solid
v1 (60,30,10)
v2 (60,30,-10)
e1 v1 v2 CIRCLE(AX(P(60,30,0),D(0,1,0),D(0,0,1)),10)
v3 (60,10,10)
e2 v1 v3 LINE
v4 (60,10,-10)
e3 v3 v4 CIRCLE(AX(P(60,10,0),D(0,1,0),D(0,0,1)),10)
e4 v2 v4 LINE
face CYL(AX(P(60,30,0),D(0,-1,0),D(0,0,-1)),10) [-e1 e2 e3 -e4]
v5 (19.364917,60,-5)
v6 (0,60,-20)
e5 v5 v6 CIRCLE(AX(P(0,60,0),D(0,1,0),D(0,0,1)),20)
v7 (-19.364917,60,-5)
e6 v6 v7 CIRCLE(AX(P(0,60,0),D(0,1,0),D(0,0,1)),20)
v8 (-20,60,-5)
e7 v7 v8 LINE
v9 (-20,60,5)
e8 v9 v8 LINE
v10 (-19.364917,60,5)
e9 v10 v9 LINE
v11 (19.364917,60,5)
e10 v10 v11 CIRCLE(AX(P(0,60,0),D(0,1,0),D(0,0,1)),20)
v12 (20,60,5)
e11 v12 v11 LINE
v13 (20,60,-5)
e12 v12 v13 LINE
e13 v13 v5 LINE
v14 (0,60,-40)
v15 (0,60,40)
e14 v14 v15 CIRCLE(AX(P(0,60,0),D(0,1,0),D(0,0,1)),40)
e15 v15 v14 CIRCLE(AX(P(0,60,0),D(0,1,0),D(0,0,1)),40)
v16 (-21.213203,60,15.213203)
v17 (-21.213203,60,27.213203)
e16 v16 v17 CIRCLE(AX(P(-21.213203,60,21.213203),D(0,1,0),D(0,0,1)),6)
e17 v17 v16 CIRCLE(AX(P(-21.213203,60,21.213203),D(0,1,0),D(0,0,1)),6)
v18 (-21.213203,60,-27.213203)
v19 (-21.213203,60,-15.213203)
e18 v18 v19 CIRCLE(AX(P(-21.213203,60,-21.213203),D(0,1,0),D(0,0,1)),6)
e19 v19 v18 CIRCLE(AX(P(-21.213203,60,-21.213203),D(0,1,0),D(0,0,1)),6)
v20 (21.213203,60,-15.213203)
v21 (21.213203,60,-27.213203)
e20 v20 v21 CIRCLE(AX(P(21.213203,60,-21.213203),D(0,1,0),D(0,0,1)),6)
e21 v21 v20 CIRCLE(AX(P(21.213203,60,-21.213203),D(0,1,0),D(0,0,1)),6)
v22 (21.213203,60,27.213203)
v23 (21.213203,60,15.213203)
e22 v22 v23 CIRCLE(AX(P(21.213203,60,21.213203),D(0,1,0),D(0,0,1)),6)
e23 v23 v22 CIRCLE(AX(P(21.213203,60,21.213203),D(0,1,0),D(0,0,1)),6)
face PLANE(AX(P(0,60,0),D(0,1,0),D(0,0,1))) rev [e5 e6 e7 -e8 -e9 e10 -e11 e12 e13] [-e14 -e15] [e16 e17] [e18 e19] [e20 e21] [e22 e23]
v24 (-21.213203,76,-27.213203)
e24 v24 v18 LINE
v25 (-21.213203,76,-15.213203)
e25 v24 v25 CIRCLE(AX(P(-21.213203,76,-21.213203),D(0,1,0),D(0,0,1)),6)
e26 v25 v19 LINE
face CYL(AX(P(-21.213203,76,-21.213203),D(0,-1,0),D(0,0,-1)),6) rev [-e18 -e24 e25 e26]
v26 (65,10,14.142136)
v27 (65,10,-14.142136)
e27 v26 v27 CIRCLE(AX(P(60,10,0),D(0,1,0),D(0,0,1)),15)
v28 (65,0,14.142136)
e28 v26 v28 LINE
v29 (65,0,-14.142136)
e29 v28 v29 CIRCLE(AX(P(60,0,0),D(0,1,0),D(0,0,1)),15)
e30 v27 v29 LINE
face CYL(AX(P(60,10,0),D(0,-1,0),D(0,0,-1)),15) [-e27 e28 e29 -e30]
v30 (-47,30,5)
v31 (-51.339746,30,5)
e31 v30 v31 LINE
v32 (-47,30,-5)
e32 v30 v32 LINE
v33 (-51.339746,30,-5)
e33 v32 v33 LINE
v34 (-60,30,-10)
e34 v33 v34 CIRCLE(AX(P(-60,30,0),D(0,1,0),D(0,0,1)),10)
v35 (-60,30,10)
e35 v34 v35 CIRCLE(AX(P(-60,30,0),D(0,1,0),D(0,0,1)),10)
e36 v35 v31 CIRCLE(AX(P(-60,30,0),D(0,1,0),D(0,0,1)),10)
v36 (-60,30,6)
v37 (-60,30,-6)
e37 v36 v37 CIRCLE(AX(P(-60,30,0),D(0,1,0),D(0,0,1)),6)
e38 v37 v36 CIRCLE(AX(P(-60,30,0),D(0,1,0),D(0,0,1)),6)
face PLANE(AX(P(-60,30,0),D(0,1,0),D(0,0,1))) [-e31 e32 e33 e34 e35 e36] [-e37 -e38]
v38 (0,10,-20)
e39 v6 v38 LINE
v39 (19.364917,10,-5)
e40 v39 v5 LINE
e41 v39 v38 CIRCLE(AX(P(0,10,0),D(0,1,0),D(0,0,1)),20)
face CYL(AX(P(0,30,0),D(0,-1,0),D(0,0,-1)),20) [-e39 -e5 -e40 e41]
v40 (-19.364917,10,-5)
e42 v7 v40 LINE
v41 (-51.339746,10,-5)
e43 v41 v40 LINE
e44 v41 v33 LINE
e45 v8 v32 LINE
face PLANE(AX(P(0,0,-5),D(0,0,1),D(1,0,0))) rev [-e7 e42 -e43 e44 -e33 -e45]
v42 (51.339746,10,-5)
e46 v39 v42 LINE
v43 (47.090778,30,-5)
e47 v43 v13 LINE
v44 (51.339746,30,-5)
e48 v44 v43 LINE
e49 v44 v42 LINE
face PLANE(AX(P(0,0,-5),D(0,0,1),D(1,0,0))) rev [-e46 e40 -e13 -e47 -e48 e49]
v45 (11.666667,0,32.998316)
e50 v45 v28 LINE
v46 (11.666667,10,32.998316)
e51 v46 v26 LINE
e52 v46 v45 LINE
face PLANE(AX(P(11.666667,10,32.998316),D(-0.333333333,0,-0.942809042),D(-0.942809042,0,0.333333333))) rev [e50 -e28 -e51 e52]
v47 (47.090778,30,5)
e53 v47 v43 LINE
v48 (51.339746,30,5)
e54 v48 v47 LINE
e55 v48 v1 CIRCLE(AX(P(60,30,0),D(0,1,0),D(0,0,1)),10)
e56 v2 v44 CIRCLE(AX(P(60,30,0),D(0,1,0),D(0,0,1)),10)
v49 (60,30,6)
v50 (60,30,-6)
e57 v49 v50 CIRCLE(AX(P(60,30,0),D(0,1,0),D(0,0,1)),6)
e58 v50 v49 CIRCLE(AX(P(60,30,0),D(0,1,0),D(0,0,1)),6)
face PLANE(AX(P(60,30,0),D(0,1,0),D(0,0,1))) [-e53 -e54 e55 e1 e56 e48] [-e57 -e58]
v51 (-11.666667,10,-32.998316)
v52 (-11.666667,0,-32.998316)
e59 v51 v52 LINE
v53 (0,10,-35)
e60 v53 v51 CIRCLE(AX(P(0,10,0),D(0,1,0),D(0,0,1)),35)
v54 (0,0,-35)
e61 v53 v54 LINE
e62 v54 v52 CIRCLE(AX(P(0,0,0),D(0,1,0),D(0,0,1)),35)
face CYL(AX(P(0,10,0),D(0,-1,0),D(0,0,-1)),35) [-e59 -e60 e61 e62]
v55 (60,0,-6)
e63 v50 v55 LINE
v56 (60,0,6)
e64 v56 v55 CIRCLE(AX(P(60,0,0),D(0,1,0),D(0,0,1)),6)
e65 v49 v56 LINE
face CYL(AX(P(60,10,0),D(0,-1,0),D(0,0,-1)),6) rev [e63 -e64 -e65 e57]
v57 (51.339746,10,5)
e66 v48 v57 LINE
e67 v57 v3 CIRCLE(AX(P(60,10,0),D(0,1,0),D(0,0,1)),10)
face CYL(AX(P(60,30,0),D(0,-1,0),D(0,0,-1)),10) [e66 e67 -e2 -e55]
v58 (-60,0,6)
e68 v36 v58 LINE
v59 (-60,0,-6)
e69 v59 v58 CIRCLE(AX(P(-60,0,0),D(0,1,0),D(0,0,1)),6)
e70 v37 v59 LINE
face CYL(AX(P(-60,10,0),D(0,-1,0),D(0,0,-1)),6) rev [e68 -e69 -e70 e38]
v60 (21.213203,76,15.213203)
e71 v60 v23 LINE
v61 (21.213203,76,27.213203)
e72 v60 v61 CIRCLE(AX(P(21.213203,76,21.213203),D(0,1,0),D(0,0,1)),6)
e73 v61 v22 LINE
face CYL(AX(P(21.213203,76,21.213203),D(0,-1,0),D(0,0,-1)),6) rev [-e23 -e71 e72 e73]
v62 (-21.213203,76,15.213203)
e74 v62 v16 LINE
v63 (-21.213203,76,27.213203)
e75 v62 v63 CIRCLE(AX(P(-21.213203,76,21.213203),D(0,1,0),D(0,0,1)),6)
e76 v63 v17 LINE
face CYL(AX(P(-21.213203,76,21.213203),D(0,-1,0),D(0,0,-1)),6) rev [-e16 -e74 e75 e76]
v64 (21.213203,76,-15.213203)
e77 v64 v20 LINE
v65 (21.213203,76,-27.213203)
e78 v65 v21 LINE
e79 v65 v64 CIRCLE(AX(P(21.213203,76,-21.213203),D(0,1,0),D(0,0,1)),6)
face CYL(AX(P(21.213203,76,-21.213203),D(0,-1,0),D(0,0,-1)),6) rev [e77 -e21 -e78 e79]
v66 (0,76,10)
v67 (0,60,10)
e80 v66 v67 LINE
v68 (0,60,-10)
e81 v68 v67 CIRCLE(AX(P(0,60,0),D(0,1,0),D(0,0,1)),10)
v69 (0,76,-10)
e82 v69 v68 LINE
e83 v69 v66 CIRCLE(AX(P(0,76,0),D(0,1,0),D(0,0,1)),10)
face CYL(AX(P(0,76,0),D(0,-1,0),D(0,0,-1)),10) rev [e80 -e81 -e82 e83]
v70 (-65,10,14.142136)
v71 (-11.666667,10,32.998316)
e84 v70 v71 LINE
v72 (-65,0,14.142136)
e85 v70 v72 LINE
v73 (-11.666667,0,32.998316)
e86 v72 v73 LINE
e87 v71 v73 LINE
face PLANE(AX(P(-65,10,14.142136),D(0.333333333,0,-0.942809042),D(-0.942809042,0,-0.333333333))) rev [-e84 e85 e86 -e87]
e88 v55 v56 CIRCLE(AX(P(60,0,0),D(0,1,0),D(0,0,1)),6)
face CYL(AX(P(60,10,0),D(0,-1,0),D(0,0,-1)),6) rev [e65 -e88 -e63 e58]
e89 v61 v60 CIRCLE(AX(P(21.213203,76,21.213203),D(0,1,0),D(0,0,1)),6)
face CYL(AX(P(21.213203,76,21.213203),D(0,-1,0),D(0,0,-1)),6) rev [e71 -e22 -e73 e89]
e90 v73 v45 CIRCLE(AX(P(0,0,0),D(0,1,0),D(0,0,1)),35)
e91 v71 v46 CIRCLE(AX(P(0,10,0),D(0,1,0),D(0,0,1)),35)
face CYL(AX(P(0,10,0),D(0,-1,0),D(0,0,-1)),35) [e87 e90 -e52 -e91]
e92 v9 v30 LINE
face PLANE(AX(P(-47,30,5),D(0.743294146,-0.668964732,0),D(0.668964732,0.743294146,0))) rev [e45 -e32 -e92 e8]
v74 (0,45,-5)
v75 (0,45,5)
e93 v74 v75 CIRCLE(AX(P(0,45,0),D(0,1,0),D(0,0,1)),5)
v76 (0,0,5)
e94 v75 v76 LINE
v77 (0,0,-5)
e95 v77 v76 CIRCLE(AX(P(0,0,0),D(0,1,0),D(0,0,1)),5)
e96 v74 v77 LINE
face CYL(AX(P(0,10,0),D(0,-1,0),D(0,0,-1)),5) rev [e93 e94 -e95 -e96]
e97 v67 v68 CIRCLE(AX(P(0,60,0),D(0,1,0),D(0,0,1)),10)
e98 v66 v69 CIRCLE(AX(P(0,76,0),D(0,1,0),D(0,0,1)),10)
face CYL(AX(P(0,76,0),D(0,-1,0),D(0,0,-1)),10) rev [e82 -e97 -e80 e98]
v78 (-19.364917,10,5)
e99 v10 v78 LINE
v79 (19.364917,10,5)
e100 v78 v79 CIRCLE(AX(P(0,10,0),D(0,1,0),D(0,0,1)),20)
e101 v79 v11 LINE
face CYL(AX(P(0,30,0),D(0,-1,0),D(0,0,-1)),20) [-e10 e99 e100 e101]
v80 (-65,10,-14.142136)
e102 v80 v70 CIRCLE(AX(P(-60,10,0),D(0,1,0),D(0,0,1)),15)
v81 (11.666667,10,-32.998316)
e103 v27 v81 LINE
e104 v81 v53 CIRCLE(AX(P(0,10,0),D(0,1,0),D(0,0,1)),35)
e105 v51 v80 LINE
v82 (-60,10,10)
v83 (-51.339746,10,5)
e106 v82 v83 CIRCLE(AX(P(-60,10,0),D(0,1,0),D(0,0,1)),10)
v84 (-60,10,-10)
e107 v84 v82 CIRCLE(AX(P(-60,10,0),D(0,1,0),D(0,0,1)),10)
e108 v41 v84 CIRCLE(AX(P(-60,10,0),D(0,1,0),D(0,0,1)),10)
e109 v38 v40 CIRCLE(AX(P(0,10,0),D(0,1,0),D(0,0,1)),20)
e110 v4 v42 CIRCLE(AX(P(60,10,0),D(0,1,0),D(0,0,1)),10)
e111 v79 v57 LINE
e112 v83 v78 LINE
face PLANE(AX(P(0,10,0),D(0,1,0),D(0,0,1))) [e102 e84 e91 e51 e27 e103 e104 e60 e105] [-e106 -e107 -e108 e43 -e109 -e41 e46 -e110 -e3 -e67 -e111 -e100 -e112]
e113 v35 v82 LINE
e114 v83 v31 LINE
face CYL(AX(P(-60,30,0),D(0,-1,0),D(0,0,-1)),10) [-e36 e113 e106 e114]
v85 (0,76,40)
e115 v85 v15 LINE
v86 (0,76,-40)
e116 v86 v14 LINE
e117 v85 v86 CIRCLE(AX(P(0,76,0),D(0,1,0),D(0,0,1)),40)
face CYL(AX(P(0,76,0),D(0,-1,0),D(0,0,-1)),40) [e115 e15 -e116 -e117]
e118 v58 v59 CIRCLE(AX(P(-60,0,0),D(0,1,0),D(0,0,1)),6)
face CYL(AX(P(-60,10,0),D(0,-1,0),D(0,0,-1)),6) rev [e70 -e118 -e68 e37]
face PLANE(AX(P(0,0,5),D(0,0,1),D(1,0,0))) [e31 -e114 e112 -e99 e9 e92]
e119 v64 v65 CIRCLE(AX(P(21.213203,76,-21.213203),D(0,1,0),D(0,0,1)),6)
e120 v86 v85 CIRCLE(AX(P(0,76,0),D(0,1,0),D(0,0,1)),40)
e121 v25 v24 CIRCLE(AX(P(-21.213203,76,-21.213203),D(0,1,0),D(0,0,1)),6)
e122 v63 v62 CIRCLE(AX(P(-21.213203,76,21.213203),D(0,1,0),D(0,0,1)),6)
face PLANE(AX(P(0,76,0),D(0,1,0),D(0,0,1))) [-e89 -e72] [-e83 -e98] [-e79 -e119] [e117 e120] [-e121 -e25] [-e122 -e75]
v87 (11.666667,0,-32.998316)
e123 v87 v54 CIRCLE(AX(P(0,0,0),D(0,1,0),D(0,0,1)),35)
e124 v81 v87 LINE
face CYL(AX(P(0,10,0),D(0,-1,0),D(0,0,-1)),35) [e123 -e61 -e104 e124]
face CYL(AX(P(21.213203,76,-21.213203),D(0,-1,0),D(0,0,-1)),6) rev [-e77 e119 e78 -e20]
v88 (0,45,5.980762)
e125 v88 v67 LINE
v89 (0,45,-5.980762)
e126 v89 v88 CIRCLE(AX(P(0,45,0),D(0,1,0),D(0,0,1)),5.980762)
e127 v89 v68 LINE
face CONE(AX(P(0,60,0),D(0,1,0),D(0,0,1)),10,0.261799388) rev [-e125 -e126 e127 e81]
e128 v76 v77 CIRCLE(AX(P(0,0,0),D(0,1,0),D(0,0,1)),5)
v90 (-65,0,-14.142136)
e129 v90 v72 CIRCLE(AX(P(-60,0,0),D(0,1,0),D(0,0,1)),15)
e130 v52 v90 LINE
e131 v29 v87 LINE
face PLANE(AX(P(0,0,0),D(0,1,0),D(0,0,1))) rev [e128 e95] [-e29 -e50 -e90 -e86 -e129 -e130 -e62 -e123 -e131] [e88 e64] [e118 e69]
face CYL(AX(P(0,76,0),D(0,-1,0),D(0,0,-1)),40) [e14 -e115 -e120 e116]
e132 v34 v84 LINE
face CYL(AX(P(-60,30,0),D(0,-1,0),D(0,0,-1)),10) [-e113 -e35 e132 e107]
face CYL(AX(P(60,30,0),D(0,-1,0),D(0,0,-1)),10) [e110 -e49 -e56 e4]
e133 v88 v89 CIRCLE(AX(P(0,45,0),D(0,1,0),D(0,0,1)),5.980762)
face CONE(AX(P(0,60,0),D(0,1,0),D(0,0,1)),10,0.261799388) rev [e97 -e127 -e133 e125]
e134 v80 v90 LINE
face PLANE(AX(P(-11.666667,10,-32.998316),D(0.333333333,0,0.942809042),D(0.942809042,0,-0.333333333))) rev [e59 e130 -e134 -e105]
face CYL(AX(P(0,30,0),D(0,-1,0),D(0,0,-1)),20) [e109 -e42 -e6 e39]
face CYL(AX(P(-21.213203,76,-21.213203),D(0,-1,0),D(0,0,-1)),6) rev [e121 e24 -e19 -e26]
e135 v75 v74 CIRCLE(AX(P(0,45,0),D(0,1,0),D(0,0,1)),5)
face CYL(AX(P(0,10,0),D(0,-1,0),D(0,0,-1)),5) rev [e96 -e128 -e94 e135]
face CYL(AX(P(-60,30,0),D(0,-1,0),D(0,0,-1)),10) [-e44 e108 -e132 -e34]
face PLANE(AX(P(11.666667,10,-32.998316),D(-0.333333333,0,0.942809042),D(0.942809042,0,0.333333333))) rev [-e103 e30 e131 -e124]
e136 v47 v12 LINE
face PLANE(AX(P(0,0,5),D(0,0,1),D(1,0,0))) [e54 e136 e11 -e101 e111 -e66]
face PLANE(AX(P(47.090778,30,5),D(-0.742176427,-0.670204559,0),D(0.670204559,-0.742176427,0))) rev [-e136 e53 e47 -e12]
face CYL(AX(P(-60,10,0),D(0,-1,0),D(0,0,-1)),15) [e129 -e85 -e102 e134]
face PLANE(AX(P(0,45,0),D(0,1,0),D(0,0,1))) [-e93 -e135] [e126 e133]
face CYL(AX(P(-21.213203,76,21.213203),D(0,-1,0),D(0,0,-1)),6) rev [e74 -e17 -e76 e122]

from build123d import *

# Parameters (mm, degrees)
BASE_FLANGE_SKETCH_R                 = 5
BASE_FLANGE_SKETCH_R_2               = 6
BASE_FLANGE_DEPTH                    = 10
PILLAR_AND_LUG_BOSSES_SKETCH_R       = 20
PILLAR_AND_LUG_BOSSES_SKETCH_R_2     = 5
PILLAR_AND_LUG_BOSSES_SKETCH_R_3     = 10
PILLAR_AND_LUG_BOSSES_SKETCH_R_4     = 6
PILLAR_AND_LUG_BOSSES_DEPTH          = 20
UPPER_PILLAR_SKETCH_R                = 20
UPPER_PILLAR_SKETCH_R_2              = 5
UPPER_PILLAR_40_DEPTH                = 30
SUPPORT_WEB_DEPTH                    = 5
TAPERED_BORE_SKETCH_R                = 10
TAPERED_BORE_20_DEPTH                = 15
TAPERED_BORE_20_DRAFT                = -15
TOP_FLANGE_SKETCH_R                  = 40
TOP_FLANGE_SKETCH_R_2                = 10
TOP_FLANGE_SKETCH_R_3                = 6
TOP_FLANGE_80_WITH_HOLES_4X_12_DEPTH = 16


with BuildPart() as part:
    # Base Flange Sketch → Base Flange (new body)
    with BuildSketch(Plane(origin=(0, 0, 0), x_dir=(1, 0, 0), z_dir=(0, 1, 0))):
        with BuildLine():
            Line((-11.666666667, 32.998316455), (-65, 14.142135624))
            ThreePointArc((-65, 14.142135624), (-75, 0), (-65, -14.142135624))
            Line((-65, -14.142135624), (-11.666666667, -32.998316455))
            ThreePointArc((-11.666666667, -32.998316455), (0, -35), (11.666666667, -32.998316455))
            Line((11.666666667, -32.998316455), (65, -14.142135624))
            ThreePointArc((65, -14.142135624), (75, 0), (65, 14.142135624))
            Line((65, 14.142135624), (11.666666667, 32.998316455))
            ThreePointArc((11.666666667, 32.998316455), (0, 35), (-11.666666667, 32.998316455))
        make_face()
        with Locations(Location((0, 0, 0), (0, 0, 270))):
            Circle(BASE_FLANGE_SKETCH_R, mode=Mode.SUBTRACT)
        with Locations(Location((-60, 0, 0), (0, 0, 270))):
            Circle(BASE_FLANGE_SKETCH_R_2, mode=Mode.SUBTRACT)
        with Locations(Location((60, 0, 0), (0, 0, 270))):
            Circle(BASE_FLANGE_SKETCH_R_2, mode=Mode.SUBTRACT)
    extrude(amount=BASE_FLANGE_DEPTH)

    # Pillar and Lug Bosses Sketch → Pillar and Lug Bosses (add)
    # profile 1 of 3: a face of its own
    with BuildSketch(Plane(origin=(0, 10, 0), x_dir=(1, 0, 0), z_dir=(0, 1, 0))):
        with Locations(Location((0, 0, 0), (0, 0, 270))):
            Circle(PILLAR_AND_LUG_BOSSES_SKETCH_R)
        with Locations(Location((0, 0, 0), (0, 0, 270))):
            Circle(PILLAR_AND_LUG_BOSSES_SKETCH_R_2, mode=Mode.SUBTRACT)
    # profile 2 of 3: a face of its own
    with BuildSketch(Plane(origin=(0, 10, 0), x_dir=(1, 0, 0), z_dir=(0, 1, 0))):
        with Locations(Location((-60, 0, 0), (0, 0, 270))):
            Circle(PILLAR_AND_LUG_BOSSES_SKETCH_R_3)
        with Locations(Location((-60, 0, 0), (0, 0, 270))):
            Circle(PILLAR_AND_LUG_BOSSES_SKETCH_R_4, mode=Mode.SUBTRACT)
    # profile 3 of 3: a face of its own
    with BuildSketch(Plane(origin=(0, 10, 0), x_dir=(1, 0, 0), z_dir=(0, 1, 0))):
        with Locations(Location((60, 0, 0), (0, 0, 270))):
            Circle(PILLAR_AND_LUG_BOSSES_SKETCH_R_3)
        with Locations(Location((60, 0, 0), (0, 0, 270))):
            Circle(PILLAR_AND_LUG_BOSSES_SKETCH_R_4, mode=Mode.SUBTRACT)
    extrude(amount=PILLAR_AND_LUG_BOSSES_DEPTH)

    # Upper Pillar Sketch → Upper Pillar Ø40 (add)
    with BuildSketch(Plane(origin=(0, 30, 0), x_dir=(1, 0, 0), z_dir=(0, 1, 0))):
        with Locations(Location((0, 0, 0), (0, 0, 270))):
            Circle(UPPER_PILLAR_SKETCH_R)
        with Locations(Location((0, 0, 0), (0, 0, 270))):
            Circle(UPPER_PILLAR_SKETCH_R_2, mode=Mode.SUBTRACT)
    extrude(amount=UPPER_PILLAR_40_DEPTH)

    # Support Web Sketch → Support Web (add, symmetric)
    with BuildSketch(Plane.XY):
        Polygon((-47, 30), (-52, 30), (-52, 10), (-16.568658107, 10), (-16.568658107, 60), (-20, 60), align=None)
        Polygon((52.090777917, 30), (47.090777917, 30), (20, 60), (17.352207011, 60), (17.352207011, 10), (52.090777917, 10), align=None)
    extrude(amount=SUPPORT_WEB_DEPTH, both=True)


with BuildPart() as tapered_bore_20_tool:
    # Tapered Bore Sketch → Tapered Bore Ø20 (with draft: the straight prism first)
    with BuildSketch(Plane(origin=(0, 60, 0), x_dir=(1, 0, 0), z_dir=(0, 1, 0))):
        Circle(TAPERED_BORE_SKETCH_R)
    extrude(amount=-TAPERED_BORE_20_DEPTH)
    # Tapered Bore Ø20: the draft: its side faces are tilted about the plane it starts from
    tapered_bore_20_sides = [tapered_bore_20_tool.faces().sort_by_distance(p)[0] for p in [
        (-10, 52.5, 0),
    ]]
    draft(tapered_bore_20_sides, Plane(origin=(0, 60, 0), x_dir=(1, 0, 0), z_dir=(0, 1, 0)), TAPERED_BORE_20_DRAFT)


with BuildPart() as part_1:
    add(part.part)

    # Tapered Bore Ø20: cut by tapered_bore_20_tool
    add(tapered_bore_20_tool.part, mode=Mode.SUBTRACT)

    # Top Flange Sketch → Top Flange Ø80 with Holes 4xØ12 (add)
    with BuildSketch(Plane(origin=(0, 60, 0), x_dir=(1, 0, 0), z_dir=(0, 1, 0))):
        with Locations(Location((0, 0, 0), (0, 0, 270))):
            Circle(TOP_FLANGE_SKETCH_R)
        with Locations(Location((0, 0, 0), (0, 0, 270))):
            Circle(TOP_FLANGE_SKETCH_R_2, mode=Mode.SUBTRACT)
        with Locations(Location((21.213203436, 21.213203436, 0), (0, 0, 270))):
            Circle(TOP_FLANGE_SKETCH_R_3, mode=Mode.SUBTRACT)
        with Locations(Location((21.213203436, -21.213203436, 0), (0, 0, 270))):
            Circle(TOP_FLANGE_SKETCH_R_3, mode=Mode.SUBTRACT)
        with Locations(Location((-21.213203436, -21.213203436, 0), (0, 0, 270))):
            Circle(TOP_FLANGE_SKETCH_R_3, mode=Mode.SUBTRACT)
        with Locations(Location((-21.213203436, 21.213203436, 0), (0, 0, 270))):
            Circle(TOP_FLANGE_SKETCH_R_3, mode=Mode.SUBTRACT)
    extrude(amount=TOP_FLANGE_80_WITH_HOLES_4X_12_DEPTH)


solid = part_1.part
